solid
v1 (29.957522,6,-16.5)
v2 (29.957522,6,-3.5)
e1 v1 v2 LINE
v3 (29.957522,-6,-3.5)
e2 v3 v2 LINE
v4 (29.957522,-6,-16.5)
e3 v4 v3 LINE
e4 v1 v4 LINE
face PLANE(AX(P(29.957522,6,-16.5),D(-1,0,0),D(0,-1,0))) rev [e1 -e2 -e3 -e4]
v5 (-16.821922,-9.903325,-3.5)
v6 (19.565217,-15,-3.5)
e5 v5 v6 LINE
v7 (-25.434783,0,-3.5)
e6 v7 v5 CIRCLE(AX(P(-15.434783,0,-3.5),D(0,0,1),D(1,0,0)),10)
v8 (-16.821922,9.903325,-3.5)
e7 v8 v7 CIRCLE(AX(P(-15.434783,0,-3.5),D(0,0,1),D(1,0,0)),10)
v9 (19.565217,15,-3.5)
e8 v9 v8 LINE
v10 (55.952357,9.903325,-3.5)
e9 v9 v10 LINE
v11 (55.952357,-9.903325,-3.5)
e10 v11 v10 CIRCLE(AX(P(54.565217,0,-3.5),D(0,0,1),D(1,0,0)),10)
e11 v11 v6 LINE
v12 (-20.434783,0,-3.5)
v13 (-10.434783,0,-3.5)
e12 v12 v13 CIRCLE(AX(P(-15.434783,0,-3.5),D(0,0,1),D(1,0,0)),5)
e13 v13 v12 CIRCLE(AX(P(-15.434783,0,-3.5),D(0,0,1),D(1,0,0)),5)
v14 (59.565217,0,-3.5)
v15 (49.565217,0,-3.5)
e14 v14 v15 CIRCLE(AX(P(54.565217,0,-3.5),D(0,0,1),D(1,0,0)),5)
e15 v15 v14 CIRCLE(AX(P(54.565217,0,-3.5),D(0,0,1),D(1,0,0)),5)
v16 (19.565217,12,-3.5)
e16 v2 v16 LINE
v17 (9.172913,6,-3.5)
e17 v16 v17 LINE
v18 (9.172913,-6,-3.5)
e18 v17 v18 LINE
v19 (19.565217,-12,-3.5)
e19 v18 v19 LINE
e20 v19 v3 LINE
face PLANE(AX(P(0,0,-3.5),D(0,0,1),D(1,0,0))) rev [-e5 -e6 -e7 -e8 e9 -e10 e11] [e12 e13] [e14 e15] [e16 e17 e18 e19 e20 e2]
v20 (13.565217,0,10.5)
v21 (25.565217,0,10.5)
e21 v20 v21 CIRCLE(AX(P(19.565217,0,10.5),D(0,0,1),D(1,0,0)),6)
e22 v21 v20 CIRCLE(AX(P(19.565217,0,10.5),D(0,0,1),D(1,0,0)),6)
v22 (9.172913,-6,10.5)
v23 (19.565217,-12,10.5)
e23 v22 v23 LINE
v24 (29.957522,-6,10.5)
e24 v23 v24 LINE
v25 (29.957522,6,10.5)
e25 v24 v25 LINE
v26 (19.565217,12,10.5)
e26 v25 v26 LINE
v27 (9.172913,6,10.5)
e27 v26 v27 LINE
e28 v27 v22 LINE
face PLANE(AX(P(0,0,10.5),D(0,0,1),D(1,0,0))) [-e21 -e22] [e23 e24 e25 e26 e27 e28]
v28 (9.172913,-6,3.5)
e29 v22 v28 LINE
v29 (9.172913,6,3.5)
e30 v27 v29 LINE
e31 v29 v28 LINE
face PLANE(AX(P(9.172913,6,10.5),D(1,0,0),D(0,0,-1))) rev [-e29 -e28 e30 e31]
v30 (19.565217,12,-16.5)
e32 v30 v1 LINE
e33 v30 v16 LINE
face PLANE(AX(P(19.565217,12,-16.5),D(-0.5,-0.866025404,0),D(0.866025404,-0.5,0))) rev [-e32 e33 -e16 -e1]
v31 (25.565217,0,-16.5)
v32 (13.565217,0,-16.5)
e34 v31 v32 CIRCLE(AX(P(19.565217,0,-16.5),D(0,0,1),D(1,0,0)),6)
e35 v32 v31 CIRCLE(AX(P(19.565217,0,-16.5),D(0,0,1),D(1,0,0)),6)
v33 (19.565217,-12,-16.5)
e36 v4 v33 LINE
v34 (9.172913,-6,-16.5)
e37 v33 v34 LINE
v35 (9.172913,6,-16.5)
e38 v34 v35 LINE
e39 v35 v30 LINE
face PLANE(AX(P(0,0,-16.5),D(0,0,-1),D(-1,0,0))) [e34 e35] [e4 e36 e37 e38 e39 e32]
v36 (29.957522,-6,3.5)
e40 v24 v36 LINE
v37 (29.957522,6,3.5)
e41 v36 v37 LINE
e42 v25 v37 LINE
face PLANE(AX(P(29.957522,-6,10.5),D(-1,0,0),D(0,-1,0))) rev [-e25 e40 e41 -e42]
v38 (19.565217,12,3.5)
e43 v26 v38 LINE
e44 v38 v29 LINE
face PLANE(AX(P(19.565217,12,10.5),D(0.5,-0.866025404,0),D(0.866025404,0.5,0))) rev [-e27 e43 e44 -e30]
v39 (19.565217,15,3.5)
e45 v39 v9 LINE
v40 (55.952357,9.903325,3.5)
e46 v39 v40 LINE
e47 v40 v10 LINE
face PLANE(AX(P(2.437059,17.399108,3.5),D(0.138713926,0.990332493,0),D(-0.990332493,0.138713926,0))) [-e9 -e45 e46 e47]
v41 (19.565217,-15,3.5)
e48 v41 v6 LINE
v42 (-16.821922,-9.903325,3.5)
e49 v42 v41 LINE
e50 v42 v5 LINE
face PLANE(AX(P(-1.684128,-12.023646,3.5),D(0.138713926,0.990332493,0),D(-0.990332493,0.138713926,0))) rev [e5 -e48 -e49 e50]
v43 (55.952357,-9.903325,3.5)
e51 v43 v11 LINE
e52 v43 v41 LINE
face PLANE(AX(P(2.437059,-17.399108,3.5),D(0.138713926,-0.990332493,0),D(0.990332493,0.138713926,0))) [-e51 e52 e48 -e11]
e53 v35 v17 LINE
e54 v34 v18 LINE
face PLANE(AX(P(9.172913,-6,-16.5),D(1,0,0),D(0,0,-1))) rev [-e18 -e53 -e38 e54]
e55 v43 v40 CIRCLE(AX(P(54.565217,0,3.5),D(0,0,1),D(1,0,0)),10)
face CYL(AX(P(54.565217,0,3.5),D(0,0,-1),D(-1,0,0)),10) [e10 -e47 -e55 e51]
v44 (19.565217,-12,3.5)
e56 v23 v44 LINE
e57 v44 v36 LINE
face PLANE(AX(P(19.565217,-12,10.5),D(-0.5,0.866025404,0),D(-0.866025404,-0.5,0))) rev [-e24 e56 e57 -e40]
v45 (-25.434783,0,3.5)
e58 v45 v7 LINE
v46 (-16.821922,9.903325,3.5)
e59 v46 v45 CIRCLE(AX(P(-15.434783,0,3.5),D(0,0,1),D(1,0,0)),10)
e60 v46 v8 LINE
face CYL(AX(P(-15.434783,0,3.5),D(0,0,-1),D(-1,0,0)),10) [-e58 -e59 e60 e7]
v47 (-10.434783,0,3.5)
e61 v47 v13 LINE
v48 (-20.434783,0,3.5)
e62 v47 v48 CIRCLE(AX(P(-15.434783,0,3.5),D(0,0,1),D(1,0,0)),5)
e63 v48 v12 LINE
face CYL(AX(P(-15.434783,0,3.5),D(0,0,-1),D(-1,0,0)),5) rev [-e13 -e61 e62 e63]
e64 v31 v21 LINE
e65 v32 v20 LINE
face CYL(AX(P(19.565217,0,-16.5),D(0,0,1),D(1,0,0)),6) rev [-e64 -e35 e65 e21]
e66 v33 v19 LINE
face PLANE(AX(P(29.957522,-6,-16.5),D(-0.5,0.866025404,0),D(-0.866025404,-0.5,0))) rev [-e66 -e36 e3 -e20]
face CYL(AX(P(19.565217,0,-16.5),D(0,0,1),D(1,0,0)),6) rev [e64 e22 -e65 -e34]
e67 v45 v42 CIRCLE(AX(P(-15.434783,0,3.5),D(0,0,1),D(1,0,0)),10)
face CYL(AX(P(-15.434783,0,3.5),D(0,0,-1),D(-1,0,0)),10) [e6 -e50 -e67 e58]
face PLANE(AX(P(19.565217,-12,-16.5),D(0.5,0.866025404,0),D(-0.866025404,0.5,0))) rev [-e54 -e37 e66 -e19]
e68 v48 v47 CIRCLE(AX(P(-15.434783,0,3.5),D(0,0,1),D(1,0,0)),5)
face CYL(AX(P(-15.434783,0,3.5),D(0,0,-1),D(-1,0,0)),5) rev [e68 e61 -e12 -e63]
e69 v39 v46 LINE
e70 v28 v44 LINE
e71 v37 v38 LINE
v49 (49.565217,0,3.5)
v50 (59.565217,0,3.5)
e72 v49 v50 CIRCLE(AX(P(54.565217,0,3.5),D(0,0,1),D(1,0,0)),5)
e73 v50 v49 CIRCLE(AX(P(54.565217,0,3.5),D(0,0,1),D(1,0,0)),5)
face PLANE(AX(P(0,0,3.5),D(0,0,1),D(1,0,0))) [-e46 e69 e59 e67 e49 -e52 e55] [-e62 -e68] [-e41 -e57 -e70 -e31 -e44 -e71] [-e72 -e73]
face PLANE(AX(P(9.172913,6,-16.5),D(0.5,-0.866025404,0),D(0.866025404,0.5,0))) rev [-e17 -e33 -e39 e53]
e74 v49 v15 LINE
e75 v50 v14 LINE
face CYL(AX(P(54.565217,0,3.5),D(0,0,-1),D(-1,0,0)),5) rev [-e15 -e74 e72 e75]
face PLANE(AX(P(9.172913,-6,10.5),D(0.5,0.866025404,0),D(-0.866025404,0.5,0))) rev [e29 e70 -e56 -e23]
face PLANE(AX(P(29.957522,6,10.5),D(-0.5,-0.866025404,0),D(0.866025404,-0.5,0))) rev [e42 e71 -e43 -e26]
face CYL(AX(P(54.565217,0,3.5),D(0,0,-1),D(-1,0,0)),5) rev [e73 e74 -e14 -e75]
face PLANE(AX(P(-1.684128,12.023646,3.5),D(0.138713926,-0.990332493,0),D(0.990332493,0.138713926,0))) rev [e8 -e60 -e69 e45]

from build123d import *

# Parameters (mm, degrees)
LINK_PLATE_PROFILE_R  = 5
LINK_PLATE_DEPTH      = 3.5
FRONT_HEX_BOSS_DEPTH  = 10.5
REAR_HEX_BOSS_DEPTH   = 16.5
CENTRE_BORE_PROFILE_R = 6
CENTRE_BORE_12_DEPTH  = 72.572811156


with BuildPart() as part:
    # Link Plate Profile → Link Plate (new, symmetric)
    with BuildSketch(Plane.XY):
        with BuildLine():
            Line((55.952356647, 9.903324931), (19.565217391, 15))
            Line((19.565217391, 15), (-16.821921865, 9.903324931))
            ThreePointArc((-16.821921865, 9.903324931), (-25.434782609, 0), (-16.821921865, -9.903324931))
            Line((-16.821921865, -9.903324931), (19.565217391, -15))
            Line((19.565217391, -15), (55.952356647, -9.903324931))
            ThreePointArc((55.952356647, -9.903324931), (64.565217391, 0), (55.952356647, 9.903324931))
        make_face()
        with Locations((-15.434782609, 0)):
            Circle(LINK_PLATE_PROFILE_R, mode=Mode.SUBTRACT)
        Polygon((9.172912546, 6), (19.565217391, 12), (29.957522237, 6), (29.957522237, -6), (19.565217391, -12), (9.172912546, -6), align=None, mode=Mode.SUBTRACT)
        with Locations((54.565217391, 0)):
            Circle(LINK_PLATE_PROFILE_R, mode=Mode.SUBTRACT)
    extrude(amount=LINK_PLATE_DEPTH, both=True)

    # Front Hex Profile → Front Hex Boss (add)
    with BuildSketch(Plane.XY):
        Polygon((9.172912546, 6), (9.172912546, -6), (19.565217391, -12), (29.957522237, -6), (29.957522237, 6), (19.565217391, 12), align=None)
    extrude(amount=FRONT_HEX_BOSS_DEPTH)

    # Rear Hex Profile → Rear Hex Boss (add)
    with BuildSketch(Plane(origin=(0, 0, 0), x_dir=(-1, 0, 0), z_dir=(0, 0, -1))):
        Polygon((-9.172912546, 6), (-19.565217391, 12), (-29.957522237, 6), (-29.957522237, -6), (-19.565217391, -12), (-9.172912546, -6), align=None)
    extrude(amount=REAR_HEX_BOSS_DEPTH)

    # Centre Bore Profile → Centre Bore Ø12 (cut, through all)
    with BuildSketch(Plane.XY.offset(10.5)):
        with Locations((19.565217391, 0)):
            Circle(CENTRE_BORE_PROFILE_R)
    extrude(amount=-CENTRE_BORE_12_DEPTH, mode=Mode.SUBTRACT)


solid = part.part
